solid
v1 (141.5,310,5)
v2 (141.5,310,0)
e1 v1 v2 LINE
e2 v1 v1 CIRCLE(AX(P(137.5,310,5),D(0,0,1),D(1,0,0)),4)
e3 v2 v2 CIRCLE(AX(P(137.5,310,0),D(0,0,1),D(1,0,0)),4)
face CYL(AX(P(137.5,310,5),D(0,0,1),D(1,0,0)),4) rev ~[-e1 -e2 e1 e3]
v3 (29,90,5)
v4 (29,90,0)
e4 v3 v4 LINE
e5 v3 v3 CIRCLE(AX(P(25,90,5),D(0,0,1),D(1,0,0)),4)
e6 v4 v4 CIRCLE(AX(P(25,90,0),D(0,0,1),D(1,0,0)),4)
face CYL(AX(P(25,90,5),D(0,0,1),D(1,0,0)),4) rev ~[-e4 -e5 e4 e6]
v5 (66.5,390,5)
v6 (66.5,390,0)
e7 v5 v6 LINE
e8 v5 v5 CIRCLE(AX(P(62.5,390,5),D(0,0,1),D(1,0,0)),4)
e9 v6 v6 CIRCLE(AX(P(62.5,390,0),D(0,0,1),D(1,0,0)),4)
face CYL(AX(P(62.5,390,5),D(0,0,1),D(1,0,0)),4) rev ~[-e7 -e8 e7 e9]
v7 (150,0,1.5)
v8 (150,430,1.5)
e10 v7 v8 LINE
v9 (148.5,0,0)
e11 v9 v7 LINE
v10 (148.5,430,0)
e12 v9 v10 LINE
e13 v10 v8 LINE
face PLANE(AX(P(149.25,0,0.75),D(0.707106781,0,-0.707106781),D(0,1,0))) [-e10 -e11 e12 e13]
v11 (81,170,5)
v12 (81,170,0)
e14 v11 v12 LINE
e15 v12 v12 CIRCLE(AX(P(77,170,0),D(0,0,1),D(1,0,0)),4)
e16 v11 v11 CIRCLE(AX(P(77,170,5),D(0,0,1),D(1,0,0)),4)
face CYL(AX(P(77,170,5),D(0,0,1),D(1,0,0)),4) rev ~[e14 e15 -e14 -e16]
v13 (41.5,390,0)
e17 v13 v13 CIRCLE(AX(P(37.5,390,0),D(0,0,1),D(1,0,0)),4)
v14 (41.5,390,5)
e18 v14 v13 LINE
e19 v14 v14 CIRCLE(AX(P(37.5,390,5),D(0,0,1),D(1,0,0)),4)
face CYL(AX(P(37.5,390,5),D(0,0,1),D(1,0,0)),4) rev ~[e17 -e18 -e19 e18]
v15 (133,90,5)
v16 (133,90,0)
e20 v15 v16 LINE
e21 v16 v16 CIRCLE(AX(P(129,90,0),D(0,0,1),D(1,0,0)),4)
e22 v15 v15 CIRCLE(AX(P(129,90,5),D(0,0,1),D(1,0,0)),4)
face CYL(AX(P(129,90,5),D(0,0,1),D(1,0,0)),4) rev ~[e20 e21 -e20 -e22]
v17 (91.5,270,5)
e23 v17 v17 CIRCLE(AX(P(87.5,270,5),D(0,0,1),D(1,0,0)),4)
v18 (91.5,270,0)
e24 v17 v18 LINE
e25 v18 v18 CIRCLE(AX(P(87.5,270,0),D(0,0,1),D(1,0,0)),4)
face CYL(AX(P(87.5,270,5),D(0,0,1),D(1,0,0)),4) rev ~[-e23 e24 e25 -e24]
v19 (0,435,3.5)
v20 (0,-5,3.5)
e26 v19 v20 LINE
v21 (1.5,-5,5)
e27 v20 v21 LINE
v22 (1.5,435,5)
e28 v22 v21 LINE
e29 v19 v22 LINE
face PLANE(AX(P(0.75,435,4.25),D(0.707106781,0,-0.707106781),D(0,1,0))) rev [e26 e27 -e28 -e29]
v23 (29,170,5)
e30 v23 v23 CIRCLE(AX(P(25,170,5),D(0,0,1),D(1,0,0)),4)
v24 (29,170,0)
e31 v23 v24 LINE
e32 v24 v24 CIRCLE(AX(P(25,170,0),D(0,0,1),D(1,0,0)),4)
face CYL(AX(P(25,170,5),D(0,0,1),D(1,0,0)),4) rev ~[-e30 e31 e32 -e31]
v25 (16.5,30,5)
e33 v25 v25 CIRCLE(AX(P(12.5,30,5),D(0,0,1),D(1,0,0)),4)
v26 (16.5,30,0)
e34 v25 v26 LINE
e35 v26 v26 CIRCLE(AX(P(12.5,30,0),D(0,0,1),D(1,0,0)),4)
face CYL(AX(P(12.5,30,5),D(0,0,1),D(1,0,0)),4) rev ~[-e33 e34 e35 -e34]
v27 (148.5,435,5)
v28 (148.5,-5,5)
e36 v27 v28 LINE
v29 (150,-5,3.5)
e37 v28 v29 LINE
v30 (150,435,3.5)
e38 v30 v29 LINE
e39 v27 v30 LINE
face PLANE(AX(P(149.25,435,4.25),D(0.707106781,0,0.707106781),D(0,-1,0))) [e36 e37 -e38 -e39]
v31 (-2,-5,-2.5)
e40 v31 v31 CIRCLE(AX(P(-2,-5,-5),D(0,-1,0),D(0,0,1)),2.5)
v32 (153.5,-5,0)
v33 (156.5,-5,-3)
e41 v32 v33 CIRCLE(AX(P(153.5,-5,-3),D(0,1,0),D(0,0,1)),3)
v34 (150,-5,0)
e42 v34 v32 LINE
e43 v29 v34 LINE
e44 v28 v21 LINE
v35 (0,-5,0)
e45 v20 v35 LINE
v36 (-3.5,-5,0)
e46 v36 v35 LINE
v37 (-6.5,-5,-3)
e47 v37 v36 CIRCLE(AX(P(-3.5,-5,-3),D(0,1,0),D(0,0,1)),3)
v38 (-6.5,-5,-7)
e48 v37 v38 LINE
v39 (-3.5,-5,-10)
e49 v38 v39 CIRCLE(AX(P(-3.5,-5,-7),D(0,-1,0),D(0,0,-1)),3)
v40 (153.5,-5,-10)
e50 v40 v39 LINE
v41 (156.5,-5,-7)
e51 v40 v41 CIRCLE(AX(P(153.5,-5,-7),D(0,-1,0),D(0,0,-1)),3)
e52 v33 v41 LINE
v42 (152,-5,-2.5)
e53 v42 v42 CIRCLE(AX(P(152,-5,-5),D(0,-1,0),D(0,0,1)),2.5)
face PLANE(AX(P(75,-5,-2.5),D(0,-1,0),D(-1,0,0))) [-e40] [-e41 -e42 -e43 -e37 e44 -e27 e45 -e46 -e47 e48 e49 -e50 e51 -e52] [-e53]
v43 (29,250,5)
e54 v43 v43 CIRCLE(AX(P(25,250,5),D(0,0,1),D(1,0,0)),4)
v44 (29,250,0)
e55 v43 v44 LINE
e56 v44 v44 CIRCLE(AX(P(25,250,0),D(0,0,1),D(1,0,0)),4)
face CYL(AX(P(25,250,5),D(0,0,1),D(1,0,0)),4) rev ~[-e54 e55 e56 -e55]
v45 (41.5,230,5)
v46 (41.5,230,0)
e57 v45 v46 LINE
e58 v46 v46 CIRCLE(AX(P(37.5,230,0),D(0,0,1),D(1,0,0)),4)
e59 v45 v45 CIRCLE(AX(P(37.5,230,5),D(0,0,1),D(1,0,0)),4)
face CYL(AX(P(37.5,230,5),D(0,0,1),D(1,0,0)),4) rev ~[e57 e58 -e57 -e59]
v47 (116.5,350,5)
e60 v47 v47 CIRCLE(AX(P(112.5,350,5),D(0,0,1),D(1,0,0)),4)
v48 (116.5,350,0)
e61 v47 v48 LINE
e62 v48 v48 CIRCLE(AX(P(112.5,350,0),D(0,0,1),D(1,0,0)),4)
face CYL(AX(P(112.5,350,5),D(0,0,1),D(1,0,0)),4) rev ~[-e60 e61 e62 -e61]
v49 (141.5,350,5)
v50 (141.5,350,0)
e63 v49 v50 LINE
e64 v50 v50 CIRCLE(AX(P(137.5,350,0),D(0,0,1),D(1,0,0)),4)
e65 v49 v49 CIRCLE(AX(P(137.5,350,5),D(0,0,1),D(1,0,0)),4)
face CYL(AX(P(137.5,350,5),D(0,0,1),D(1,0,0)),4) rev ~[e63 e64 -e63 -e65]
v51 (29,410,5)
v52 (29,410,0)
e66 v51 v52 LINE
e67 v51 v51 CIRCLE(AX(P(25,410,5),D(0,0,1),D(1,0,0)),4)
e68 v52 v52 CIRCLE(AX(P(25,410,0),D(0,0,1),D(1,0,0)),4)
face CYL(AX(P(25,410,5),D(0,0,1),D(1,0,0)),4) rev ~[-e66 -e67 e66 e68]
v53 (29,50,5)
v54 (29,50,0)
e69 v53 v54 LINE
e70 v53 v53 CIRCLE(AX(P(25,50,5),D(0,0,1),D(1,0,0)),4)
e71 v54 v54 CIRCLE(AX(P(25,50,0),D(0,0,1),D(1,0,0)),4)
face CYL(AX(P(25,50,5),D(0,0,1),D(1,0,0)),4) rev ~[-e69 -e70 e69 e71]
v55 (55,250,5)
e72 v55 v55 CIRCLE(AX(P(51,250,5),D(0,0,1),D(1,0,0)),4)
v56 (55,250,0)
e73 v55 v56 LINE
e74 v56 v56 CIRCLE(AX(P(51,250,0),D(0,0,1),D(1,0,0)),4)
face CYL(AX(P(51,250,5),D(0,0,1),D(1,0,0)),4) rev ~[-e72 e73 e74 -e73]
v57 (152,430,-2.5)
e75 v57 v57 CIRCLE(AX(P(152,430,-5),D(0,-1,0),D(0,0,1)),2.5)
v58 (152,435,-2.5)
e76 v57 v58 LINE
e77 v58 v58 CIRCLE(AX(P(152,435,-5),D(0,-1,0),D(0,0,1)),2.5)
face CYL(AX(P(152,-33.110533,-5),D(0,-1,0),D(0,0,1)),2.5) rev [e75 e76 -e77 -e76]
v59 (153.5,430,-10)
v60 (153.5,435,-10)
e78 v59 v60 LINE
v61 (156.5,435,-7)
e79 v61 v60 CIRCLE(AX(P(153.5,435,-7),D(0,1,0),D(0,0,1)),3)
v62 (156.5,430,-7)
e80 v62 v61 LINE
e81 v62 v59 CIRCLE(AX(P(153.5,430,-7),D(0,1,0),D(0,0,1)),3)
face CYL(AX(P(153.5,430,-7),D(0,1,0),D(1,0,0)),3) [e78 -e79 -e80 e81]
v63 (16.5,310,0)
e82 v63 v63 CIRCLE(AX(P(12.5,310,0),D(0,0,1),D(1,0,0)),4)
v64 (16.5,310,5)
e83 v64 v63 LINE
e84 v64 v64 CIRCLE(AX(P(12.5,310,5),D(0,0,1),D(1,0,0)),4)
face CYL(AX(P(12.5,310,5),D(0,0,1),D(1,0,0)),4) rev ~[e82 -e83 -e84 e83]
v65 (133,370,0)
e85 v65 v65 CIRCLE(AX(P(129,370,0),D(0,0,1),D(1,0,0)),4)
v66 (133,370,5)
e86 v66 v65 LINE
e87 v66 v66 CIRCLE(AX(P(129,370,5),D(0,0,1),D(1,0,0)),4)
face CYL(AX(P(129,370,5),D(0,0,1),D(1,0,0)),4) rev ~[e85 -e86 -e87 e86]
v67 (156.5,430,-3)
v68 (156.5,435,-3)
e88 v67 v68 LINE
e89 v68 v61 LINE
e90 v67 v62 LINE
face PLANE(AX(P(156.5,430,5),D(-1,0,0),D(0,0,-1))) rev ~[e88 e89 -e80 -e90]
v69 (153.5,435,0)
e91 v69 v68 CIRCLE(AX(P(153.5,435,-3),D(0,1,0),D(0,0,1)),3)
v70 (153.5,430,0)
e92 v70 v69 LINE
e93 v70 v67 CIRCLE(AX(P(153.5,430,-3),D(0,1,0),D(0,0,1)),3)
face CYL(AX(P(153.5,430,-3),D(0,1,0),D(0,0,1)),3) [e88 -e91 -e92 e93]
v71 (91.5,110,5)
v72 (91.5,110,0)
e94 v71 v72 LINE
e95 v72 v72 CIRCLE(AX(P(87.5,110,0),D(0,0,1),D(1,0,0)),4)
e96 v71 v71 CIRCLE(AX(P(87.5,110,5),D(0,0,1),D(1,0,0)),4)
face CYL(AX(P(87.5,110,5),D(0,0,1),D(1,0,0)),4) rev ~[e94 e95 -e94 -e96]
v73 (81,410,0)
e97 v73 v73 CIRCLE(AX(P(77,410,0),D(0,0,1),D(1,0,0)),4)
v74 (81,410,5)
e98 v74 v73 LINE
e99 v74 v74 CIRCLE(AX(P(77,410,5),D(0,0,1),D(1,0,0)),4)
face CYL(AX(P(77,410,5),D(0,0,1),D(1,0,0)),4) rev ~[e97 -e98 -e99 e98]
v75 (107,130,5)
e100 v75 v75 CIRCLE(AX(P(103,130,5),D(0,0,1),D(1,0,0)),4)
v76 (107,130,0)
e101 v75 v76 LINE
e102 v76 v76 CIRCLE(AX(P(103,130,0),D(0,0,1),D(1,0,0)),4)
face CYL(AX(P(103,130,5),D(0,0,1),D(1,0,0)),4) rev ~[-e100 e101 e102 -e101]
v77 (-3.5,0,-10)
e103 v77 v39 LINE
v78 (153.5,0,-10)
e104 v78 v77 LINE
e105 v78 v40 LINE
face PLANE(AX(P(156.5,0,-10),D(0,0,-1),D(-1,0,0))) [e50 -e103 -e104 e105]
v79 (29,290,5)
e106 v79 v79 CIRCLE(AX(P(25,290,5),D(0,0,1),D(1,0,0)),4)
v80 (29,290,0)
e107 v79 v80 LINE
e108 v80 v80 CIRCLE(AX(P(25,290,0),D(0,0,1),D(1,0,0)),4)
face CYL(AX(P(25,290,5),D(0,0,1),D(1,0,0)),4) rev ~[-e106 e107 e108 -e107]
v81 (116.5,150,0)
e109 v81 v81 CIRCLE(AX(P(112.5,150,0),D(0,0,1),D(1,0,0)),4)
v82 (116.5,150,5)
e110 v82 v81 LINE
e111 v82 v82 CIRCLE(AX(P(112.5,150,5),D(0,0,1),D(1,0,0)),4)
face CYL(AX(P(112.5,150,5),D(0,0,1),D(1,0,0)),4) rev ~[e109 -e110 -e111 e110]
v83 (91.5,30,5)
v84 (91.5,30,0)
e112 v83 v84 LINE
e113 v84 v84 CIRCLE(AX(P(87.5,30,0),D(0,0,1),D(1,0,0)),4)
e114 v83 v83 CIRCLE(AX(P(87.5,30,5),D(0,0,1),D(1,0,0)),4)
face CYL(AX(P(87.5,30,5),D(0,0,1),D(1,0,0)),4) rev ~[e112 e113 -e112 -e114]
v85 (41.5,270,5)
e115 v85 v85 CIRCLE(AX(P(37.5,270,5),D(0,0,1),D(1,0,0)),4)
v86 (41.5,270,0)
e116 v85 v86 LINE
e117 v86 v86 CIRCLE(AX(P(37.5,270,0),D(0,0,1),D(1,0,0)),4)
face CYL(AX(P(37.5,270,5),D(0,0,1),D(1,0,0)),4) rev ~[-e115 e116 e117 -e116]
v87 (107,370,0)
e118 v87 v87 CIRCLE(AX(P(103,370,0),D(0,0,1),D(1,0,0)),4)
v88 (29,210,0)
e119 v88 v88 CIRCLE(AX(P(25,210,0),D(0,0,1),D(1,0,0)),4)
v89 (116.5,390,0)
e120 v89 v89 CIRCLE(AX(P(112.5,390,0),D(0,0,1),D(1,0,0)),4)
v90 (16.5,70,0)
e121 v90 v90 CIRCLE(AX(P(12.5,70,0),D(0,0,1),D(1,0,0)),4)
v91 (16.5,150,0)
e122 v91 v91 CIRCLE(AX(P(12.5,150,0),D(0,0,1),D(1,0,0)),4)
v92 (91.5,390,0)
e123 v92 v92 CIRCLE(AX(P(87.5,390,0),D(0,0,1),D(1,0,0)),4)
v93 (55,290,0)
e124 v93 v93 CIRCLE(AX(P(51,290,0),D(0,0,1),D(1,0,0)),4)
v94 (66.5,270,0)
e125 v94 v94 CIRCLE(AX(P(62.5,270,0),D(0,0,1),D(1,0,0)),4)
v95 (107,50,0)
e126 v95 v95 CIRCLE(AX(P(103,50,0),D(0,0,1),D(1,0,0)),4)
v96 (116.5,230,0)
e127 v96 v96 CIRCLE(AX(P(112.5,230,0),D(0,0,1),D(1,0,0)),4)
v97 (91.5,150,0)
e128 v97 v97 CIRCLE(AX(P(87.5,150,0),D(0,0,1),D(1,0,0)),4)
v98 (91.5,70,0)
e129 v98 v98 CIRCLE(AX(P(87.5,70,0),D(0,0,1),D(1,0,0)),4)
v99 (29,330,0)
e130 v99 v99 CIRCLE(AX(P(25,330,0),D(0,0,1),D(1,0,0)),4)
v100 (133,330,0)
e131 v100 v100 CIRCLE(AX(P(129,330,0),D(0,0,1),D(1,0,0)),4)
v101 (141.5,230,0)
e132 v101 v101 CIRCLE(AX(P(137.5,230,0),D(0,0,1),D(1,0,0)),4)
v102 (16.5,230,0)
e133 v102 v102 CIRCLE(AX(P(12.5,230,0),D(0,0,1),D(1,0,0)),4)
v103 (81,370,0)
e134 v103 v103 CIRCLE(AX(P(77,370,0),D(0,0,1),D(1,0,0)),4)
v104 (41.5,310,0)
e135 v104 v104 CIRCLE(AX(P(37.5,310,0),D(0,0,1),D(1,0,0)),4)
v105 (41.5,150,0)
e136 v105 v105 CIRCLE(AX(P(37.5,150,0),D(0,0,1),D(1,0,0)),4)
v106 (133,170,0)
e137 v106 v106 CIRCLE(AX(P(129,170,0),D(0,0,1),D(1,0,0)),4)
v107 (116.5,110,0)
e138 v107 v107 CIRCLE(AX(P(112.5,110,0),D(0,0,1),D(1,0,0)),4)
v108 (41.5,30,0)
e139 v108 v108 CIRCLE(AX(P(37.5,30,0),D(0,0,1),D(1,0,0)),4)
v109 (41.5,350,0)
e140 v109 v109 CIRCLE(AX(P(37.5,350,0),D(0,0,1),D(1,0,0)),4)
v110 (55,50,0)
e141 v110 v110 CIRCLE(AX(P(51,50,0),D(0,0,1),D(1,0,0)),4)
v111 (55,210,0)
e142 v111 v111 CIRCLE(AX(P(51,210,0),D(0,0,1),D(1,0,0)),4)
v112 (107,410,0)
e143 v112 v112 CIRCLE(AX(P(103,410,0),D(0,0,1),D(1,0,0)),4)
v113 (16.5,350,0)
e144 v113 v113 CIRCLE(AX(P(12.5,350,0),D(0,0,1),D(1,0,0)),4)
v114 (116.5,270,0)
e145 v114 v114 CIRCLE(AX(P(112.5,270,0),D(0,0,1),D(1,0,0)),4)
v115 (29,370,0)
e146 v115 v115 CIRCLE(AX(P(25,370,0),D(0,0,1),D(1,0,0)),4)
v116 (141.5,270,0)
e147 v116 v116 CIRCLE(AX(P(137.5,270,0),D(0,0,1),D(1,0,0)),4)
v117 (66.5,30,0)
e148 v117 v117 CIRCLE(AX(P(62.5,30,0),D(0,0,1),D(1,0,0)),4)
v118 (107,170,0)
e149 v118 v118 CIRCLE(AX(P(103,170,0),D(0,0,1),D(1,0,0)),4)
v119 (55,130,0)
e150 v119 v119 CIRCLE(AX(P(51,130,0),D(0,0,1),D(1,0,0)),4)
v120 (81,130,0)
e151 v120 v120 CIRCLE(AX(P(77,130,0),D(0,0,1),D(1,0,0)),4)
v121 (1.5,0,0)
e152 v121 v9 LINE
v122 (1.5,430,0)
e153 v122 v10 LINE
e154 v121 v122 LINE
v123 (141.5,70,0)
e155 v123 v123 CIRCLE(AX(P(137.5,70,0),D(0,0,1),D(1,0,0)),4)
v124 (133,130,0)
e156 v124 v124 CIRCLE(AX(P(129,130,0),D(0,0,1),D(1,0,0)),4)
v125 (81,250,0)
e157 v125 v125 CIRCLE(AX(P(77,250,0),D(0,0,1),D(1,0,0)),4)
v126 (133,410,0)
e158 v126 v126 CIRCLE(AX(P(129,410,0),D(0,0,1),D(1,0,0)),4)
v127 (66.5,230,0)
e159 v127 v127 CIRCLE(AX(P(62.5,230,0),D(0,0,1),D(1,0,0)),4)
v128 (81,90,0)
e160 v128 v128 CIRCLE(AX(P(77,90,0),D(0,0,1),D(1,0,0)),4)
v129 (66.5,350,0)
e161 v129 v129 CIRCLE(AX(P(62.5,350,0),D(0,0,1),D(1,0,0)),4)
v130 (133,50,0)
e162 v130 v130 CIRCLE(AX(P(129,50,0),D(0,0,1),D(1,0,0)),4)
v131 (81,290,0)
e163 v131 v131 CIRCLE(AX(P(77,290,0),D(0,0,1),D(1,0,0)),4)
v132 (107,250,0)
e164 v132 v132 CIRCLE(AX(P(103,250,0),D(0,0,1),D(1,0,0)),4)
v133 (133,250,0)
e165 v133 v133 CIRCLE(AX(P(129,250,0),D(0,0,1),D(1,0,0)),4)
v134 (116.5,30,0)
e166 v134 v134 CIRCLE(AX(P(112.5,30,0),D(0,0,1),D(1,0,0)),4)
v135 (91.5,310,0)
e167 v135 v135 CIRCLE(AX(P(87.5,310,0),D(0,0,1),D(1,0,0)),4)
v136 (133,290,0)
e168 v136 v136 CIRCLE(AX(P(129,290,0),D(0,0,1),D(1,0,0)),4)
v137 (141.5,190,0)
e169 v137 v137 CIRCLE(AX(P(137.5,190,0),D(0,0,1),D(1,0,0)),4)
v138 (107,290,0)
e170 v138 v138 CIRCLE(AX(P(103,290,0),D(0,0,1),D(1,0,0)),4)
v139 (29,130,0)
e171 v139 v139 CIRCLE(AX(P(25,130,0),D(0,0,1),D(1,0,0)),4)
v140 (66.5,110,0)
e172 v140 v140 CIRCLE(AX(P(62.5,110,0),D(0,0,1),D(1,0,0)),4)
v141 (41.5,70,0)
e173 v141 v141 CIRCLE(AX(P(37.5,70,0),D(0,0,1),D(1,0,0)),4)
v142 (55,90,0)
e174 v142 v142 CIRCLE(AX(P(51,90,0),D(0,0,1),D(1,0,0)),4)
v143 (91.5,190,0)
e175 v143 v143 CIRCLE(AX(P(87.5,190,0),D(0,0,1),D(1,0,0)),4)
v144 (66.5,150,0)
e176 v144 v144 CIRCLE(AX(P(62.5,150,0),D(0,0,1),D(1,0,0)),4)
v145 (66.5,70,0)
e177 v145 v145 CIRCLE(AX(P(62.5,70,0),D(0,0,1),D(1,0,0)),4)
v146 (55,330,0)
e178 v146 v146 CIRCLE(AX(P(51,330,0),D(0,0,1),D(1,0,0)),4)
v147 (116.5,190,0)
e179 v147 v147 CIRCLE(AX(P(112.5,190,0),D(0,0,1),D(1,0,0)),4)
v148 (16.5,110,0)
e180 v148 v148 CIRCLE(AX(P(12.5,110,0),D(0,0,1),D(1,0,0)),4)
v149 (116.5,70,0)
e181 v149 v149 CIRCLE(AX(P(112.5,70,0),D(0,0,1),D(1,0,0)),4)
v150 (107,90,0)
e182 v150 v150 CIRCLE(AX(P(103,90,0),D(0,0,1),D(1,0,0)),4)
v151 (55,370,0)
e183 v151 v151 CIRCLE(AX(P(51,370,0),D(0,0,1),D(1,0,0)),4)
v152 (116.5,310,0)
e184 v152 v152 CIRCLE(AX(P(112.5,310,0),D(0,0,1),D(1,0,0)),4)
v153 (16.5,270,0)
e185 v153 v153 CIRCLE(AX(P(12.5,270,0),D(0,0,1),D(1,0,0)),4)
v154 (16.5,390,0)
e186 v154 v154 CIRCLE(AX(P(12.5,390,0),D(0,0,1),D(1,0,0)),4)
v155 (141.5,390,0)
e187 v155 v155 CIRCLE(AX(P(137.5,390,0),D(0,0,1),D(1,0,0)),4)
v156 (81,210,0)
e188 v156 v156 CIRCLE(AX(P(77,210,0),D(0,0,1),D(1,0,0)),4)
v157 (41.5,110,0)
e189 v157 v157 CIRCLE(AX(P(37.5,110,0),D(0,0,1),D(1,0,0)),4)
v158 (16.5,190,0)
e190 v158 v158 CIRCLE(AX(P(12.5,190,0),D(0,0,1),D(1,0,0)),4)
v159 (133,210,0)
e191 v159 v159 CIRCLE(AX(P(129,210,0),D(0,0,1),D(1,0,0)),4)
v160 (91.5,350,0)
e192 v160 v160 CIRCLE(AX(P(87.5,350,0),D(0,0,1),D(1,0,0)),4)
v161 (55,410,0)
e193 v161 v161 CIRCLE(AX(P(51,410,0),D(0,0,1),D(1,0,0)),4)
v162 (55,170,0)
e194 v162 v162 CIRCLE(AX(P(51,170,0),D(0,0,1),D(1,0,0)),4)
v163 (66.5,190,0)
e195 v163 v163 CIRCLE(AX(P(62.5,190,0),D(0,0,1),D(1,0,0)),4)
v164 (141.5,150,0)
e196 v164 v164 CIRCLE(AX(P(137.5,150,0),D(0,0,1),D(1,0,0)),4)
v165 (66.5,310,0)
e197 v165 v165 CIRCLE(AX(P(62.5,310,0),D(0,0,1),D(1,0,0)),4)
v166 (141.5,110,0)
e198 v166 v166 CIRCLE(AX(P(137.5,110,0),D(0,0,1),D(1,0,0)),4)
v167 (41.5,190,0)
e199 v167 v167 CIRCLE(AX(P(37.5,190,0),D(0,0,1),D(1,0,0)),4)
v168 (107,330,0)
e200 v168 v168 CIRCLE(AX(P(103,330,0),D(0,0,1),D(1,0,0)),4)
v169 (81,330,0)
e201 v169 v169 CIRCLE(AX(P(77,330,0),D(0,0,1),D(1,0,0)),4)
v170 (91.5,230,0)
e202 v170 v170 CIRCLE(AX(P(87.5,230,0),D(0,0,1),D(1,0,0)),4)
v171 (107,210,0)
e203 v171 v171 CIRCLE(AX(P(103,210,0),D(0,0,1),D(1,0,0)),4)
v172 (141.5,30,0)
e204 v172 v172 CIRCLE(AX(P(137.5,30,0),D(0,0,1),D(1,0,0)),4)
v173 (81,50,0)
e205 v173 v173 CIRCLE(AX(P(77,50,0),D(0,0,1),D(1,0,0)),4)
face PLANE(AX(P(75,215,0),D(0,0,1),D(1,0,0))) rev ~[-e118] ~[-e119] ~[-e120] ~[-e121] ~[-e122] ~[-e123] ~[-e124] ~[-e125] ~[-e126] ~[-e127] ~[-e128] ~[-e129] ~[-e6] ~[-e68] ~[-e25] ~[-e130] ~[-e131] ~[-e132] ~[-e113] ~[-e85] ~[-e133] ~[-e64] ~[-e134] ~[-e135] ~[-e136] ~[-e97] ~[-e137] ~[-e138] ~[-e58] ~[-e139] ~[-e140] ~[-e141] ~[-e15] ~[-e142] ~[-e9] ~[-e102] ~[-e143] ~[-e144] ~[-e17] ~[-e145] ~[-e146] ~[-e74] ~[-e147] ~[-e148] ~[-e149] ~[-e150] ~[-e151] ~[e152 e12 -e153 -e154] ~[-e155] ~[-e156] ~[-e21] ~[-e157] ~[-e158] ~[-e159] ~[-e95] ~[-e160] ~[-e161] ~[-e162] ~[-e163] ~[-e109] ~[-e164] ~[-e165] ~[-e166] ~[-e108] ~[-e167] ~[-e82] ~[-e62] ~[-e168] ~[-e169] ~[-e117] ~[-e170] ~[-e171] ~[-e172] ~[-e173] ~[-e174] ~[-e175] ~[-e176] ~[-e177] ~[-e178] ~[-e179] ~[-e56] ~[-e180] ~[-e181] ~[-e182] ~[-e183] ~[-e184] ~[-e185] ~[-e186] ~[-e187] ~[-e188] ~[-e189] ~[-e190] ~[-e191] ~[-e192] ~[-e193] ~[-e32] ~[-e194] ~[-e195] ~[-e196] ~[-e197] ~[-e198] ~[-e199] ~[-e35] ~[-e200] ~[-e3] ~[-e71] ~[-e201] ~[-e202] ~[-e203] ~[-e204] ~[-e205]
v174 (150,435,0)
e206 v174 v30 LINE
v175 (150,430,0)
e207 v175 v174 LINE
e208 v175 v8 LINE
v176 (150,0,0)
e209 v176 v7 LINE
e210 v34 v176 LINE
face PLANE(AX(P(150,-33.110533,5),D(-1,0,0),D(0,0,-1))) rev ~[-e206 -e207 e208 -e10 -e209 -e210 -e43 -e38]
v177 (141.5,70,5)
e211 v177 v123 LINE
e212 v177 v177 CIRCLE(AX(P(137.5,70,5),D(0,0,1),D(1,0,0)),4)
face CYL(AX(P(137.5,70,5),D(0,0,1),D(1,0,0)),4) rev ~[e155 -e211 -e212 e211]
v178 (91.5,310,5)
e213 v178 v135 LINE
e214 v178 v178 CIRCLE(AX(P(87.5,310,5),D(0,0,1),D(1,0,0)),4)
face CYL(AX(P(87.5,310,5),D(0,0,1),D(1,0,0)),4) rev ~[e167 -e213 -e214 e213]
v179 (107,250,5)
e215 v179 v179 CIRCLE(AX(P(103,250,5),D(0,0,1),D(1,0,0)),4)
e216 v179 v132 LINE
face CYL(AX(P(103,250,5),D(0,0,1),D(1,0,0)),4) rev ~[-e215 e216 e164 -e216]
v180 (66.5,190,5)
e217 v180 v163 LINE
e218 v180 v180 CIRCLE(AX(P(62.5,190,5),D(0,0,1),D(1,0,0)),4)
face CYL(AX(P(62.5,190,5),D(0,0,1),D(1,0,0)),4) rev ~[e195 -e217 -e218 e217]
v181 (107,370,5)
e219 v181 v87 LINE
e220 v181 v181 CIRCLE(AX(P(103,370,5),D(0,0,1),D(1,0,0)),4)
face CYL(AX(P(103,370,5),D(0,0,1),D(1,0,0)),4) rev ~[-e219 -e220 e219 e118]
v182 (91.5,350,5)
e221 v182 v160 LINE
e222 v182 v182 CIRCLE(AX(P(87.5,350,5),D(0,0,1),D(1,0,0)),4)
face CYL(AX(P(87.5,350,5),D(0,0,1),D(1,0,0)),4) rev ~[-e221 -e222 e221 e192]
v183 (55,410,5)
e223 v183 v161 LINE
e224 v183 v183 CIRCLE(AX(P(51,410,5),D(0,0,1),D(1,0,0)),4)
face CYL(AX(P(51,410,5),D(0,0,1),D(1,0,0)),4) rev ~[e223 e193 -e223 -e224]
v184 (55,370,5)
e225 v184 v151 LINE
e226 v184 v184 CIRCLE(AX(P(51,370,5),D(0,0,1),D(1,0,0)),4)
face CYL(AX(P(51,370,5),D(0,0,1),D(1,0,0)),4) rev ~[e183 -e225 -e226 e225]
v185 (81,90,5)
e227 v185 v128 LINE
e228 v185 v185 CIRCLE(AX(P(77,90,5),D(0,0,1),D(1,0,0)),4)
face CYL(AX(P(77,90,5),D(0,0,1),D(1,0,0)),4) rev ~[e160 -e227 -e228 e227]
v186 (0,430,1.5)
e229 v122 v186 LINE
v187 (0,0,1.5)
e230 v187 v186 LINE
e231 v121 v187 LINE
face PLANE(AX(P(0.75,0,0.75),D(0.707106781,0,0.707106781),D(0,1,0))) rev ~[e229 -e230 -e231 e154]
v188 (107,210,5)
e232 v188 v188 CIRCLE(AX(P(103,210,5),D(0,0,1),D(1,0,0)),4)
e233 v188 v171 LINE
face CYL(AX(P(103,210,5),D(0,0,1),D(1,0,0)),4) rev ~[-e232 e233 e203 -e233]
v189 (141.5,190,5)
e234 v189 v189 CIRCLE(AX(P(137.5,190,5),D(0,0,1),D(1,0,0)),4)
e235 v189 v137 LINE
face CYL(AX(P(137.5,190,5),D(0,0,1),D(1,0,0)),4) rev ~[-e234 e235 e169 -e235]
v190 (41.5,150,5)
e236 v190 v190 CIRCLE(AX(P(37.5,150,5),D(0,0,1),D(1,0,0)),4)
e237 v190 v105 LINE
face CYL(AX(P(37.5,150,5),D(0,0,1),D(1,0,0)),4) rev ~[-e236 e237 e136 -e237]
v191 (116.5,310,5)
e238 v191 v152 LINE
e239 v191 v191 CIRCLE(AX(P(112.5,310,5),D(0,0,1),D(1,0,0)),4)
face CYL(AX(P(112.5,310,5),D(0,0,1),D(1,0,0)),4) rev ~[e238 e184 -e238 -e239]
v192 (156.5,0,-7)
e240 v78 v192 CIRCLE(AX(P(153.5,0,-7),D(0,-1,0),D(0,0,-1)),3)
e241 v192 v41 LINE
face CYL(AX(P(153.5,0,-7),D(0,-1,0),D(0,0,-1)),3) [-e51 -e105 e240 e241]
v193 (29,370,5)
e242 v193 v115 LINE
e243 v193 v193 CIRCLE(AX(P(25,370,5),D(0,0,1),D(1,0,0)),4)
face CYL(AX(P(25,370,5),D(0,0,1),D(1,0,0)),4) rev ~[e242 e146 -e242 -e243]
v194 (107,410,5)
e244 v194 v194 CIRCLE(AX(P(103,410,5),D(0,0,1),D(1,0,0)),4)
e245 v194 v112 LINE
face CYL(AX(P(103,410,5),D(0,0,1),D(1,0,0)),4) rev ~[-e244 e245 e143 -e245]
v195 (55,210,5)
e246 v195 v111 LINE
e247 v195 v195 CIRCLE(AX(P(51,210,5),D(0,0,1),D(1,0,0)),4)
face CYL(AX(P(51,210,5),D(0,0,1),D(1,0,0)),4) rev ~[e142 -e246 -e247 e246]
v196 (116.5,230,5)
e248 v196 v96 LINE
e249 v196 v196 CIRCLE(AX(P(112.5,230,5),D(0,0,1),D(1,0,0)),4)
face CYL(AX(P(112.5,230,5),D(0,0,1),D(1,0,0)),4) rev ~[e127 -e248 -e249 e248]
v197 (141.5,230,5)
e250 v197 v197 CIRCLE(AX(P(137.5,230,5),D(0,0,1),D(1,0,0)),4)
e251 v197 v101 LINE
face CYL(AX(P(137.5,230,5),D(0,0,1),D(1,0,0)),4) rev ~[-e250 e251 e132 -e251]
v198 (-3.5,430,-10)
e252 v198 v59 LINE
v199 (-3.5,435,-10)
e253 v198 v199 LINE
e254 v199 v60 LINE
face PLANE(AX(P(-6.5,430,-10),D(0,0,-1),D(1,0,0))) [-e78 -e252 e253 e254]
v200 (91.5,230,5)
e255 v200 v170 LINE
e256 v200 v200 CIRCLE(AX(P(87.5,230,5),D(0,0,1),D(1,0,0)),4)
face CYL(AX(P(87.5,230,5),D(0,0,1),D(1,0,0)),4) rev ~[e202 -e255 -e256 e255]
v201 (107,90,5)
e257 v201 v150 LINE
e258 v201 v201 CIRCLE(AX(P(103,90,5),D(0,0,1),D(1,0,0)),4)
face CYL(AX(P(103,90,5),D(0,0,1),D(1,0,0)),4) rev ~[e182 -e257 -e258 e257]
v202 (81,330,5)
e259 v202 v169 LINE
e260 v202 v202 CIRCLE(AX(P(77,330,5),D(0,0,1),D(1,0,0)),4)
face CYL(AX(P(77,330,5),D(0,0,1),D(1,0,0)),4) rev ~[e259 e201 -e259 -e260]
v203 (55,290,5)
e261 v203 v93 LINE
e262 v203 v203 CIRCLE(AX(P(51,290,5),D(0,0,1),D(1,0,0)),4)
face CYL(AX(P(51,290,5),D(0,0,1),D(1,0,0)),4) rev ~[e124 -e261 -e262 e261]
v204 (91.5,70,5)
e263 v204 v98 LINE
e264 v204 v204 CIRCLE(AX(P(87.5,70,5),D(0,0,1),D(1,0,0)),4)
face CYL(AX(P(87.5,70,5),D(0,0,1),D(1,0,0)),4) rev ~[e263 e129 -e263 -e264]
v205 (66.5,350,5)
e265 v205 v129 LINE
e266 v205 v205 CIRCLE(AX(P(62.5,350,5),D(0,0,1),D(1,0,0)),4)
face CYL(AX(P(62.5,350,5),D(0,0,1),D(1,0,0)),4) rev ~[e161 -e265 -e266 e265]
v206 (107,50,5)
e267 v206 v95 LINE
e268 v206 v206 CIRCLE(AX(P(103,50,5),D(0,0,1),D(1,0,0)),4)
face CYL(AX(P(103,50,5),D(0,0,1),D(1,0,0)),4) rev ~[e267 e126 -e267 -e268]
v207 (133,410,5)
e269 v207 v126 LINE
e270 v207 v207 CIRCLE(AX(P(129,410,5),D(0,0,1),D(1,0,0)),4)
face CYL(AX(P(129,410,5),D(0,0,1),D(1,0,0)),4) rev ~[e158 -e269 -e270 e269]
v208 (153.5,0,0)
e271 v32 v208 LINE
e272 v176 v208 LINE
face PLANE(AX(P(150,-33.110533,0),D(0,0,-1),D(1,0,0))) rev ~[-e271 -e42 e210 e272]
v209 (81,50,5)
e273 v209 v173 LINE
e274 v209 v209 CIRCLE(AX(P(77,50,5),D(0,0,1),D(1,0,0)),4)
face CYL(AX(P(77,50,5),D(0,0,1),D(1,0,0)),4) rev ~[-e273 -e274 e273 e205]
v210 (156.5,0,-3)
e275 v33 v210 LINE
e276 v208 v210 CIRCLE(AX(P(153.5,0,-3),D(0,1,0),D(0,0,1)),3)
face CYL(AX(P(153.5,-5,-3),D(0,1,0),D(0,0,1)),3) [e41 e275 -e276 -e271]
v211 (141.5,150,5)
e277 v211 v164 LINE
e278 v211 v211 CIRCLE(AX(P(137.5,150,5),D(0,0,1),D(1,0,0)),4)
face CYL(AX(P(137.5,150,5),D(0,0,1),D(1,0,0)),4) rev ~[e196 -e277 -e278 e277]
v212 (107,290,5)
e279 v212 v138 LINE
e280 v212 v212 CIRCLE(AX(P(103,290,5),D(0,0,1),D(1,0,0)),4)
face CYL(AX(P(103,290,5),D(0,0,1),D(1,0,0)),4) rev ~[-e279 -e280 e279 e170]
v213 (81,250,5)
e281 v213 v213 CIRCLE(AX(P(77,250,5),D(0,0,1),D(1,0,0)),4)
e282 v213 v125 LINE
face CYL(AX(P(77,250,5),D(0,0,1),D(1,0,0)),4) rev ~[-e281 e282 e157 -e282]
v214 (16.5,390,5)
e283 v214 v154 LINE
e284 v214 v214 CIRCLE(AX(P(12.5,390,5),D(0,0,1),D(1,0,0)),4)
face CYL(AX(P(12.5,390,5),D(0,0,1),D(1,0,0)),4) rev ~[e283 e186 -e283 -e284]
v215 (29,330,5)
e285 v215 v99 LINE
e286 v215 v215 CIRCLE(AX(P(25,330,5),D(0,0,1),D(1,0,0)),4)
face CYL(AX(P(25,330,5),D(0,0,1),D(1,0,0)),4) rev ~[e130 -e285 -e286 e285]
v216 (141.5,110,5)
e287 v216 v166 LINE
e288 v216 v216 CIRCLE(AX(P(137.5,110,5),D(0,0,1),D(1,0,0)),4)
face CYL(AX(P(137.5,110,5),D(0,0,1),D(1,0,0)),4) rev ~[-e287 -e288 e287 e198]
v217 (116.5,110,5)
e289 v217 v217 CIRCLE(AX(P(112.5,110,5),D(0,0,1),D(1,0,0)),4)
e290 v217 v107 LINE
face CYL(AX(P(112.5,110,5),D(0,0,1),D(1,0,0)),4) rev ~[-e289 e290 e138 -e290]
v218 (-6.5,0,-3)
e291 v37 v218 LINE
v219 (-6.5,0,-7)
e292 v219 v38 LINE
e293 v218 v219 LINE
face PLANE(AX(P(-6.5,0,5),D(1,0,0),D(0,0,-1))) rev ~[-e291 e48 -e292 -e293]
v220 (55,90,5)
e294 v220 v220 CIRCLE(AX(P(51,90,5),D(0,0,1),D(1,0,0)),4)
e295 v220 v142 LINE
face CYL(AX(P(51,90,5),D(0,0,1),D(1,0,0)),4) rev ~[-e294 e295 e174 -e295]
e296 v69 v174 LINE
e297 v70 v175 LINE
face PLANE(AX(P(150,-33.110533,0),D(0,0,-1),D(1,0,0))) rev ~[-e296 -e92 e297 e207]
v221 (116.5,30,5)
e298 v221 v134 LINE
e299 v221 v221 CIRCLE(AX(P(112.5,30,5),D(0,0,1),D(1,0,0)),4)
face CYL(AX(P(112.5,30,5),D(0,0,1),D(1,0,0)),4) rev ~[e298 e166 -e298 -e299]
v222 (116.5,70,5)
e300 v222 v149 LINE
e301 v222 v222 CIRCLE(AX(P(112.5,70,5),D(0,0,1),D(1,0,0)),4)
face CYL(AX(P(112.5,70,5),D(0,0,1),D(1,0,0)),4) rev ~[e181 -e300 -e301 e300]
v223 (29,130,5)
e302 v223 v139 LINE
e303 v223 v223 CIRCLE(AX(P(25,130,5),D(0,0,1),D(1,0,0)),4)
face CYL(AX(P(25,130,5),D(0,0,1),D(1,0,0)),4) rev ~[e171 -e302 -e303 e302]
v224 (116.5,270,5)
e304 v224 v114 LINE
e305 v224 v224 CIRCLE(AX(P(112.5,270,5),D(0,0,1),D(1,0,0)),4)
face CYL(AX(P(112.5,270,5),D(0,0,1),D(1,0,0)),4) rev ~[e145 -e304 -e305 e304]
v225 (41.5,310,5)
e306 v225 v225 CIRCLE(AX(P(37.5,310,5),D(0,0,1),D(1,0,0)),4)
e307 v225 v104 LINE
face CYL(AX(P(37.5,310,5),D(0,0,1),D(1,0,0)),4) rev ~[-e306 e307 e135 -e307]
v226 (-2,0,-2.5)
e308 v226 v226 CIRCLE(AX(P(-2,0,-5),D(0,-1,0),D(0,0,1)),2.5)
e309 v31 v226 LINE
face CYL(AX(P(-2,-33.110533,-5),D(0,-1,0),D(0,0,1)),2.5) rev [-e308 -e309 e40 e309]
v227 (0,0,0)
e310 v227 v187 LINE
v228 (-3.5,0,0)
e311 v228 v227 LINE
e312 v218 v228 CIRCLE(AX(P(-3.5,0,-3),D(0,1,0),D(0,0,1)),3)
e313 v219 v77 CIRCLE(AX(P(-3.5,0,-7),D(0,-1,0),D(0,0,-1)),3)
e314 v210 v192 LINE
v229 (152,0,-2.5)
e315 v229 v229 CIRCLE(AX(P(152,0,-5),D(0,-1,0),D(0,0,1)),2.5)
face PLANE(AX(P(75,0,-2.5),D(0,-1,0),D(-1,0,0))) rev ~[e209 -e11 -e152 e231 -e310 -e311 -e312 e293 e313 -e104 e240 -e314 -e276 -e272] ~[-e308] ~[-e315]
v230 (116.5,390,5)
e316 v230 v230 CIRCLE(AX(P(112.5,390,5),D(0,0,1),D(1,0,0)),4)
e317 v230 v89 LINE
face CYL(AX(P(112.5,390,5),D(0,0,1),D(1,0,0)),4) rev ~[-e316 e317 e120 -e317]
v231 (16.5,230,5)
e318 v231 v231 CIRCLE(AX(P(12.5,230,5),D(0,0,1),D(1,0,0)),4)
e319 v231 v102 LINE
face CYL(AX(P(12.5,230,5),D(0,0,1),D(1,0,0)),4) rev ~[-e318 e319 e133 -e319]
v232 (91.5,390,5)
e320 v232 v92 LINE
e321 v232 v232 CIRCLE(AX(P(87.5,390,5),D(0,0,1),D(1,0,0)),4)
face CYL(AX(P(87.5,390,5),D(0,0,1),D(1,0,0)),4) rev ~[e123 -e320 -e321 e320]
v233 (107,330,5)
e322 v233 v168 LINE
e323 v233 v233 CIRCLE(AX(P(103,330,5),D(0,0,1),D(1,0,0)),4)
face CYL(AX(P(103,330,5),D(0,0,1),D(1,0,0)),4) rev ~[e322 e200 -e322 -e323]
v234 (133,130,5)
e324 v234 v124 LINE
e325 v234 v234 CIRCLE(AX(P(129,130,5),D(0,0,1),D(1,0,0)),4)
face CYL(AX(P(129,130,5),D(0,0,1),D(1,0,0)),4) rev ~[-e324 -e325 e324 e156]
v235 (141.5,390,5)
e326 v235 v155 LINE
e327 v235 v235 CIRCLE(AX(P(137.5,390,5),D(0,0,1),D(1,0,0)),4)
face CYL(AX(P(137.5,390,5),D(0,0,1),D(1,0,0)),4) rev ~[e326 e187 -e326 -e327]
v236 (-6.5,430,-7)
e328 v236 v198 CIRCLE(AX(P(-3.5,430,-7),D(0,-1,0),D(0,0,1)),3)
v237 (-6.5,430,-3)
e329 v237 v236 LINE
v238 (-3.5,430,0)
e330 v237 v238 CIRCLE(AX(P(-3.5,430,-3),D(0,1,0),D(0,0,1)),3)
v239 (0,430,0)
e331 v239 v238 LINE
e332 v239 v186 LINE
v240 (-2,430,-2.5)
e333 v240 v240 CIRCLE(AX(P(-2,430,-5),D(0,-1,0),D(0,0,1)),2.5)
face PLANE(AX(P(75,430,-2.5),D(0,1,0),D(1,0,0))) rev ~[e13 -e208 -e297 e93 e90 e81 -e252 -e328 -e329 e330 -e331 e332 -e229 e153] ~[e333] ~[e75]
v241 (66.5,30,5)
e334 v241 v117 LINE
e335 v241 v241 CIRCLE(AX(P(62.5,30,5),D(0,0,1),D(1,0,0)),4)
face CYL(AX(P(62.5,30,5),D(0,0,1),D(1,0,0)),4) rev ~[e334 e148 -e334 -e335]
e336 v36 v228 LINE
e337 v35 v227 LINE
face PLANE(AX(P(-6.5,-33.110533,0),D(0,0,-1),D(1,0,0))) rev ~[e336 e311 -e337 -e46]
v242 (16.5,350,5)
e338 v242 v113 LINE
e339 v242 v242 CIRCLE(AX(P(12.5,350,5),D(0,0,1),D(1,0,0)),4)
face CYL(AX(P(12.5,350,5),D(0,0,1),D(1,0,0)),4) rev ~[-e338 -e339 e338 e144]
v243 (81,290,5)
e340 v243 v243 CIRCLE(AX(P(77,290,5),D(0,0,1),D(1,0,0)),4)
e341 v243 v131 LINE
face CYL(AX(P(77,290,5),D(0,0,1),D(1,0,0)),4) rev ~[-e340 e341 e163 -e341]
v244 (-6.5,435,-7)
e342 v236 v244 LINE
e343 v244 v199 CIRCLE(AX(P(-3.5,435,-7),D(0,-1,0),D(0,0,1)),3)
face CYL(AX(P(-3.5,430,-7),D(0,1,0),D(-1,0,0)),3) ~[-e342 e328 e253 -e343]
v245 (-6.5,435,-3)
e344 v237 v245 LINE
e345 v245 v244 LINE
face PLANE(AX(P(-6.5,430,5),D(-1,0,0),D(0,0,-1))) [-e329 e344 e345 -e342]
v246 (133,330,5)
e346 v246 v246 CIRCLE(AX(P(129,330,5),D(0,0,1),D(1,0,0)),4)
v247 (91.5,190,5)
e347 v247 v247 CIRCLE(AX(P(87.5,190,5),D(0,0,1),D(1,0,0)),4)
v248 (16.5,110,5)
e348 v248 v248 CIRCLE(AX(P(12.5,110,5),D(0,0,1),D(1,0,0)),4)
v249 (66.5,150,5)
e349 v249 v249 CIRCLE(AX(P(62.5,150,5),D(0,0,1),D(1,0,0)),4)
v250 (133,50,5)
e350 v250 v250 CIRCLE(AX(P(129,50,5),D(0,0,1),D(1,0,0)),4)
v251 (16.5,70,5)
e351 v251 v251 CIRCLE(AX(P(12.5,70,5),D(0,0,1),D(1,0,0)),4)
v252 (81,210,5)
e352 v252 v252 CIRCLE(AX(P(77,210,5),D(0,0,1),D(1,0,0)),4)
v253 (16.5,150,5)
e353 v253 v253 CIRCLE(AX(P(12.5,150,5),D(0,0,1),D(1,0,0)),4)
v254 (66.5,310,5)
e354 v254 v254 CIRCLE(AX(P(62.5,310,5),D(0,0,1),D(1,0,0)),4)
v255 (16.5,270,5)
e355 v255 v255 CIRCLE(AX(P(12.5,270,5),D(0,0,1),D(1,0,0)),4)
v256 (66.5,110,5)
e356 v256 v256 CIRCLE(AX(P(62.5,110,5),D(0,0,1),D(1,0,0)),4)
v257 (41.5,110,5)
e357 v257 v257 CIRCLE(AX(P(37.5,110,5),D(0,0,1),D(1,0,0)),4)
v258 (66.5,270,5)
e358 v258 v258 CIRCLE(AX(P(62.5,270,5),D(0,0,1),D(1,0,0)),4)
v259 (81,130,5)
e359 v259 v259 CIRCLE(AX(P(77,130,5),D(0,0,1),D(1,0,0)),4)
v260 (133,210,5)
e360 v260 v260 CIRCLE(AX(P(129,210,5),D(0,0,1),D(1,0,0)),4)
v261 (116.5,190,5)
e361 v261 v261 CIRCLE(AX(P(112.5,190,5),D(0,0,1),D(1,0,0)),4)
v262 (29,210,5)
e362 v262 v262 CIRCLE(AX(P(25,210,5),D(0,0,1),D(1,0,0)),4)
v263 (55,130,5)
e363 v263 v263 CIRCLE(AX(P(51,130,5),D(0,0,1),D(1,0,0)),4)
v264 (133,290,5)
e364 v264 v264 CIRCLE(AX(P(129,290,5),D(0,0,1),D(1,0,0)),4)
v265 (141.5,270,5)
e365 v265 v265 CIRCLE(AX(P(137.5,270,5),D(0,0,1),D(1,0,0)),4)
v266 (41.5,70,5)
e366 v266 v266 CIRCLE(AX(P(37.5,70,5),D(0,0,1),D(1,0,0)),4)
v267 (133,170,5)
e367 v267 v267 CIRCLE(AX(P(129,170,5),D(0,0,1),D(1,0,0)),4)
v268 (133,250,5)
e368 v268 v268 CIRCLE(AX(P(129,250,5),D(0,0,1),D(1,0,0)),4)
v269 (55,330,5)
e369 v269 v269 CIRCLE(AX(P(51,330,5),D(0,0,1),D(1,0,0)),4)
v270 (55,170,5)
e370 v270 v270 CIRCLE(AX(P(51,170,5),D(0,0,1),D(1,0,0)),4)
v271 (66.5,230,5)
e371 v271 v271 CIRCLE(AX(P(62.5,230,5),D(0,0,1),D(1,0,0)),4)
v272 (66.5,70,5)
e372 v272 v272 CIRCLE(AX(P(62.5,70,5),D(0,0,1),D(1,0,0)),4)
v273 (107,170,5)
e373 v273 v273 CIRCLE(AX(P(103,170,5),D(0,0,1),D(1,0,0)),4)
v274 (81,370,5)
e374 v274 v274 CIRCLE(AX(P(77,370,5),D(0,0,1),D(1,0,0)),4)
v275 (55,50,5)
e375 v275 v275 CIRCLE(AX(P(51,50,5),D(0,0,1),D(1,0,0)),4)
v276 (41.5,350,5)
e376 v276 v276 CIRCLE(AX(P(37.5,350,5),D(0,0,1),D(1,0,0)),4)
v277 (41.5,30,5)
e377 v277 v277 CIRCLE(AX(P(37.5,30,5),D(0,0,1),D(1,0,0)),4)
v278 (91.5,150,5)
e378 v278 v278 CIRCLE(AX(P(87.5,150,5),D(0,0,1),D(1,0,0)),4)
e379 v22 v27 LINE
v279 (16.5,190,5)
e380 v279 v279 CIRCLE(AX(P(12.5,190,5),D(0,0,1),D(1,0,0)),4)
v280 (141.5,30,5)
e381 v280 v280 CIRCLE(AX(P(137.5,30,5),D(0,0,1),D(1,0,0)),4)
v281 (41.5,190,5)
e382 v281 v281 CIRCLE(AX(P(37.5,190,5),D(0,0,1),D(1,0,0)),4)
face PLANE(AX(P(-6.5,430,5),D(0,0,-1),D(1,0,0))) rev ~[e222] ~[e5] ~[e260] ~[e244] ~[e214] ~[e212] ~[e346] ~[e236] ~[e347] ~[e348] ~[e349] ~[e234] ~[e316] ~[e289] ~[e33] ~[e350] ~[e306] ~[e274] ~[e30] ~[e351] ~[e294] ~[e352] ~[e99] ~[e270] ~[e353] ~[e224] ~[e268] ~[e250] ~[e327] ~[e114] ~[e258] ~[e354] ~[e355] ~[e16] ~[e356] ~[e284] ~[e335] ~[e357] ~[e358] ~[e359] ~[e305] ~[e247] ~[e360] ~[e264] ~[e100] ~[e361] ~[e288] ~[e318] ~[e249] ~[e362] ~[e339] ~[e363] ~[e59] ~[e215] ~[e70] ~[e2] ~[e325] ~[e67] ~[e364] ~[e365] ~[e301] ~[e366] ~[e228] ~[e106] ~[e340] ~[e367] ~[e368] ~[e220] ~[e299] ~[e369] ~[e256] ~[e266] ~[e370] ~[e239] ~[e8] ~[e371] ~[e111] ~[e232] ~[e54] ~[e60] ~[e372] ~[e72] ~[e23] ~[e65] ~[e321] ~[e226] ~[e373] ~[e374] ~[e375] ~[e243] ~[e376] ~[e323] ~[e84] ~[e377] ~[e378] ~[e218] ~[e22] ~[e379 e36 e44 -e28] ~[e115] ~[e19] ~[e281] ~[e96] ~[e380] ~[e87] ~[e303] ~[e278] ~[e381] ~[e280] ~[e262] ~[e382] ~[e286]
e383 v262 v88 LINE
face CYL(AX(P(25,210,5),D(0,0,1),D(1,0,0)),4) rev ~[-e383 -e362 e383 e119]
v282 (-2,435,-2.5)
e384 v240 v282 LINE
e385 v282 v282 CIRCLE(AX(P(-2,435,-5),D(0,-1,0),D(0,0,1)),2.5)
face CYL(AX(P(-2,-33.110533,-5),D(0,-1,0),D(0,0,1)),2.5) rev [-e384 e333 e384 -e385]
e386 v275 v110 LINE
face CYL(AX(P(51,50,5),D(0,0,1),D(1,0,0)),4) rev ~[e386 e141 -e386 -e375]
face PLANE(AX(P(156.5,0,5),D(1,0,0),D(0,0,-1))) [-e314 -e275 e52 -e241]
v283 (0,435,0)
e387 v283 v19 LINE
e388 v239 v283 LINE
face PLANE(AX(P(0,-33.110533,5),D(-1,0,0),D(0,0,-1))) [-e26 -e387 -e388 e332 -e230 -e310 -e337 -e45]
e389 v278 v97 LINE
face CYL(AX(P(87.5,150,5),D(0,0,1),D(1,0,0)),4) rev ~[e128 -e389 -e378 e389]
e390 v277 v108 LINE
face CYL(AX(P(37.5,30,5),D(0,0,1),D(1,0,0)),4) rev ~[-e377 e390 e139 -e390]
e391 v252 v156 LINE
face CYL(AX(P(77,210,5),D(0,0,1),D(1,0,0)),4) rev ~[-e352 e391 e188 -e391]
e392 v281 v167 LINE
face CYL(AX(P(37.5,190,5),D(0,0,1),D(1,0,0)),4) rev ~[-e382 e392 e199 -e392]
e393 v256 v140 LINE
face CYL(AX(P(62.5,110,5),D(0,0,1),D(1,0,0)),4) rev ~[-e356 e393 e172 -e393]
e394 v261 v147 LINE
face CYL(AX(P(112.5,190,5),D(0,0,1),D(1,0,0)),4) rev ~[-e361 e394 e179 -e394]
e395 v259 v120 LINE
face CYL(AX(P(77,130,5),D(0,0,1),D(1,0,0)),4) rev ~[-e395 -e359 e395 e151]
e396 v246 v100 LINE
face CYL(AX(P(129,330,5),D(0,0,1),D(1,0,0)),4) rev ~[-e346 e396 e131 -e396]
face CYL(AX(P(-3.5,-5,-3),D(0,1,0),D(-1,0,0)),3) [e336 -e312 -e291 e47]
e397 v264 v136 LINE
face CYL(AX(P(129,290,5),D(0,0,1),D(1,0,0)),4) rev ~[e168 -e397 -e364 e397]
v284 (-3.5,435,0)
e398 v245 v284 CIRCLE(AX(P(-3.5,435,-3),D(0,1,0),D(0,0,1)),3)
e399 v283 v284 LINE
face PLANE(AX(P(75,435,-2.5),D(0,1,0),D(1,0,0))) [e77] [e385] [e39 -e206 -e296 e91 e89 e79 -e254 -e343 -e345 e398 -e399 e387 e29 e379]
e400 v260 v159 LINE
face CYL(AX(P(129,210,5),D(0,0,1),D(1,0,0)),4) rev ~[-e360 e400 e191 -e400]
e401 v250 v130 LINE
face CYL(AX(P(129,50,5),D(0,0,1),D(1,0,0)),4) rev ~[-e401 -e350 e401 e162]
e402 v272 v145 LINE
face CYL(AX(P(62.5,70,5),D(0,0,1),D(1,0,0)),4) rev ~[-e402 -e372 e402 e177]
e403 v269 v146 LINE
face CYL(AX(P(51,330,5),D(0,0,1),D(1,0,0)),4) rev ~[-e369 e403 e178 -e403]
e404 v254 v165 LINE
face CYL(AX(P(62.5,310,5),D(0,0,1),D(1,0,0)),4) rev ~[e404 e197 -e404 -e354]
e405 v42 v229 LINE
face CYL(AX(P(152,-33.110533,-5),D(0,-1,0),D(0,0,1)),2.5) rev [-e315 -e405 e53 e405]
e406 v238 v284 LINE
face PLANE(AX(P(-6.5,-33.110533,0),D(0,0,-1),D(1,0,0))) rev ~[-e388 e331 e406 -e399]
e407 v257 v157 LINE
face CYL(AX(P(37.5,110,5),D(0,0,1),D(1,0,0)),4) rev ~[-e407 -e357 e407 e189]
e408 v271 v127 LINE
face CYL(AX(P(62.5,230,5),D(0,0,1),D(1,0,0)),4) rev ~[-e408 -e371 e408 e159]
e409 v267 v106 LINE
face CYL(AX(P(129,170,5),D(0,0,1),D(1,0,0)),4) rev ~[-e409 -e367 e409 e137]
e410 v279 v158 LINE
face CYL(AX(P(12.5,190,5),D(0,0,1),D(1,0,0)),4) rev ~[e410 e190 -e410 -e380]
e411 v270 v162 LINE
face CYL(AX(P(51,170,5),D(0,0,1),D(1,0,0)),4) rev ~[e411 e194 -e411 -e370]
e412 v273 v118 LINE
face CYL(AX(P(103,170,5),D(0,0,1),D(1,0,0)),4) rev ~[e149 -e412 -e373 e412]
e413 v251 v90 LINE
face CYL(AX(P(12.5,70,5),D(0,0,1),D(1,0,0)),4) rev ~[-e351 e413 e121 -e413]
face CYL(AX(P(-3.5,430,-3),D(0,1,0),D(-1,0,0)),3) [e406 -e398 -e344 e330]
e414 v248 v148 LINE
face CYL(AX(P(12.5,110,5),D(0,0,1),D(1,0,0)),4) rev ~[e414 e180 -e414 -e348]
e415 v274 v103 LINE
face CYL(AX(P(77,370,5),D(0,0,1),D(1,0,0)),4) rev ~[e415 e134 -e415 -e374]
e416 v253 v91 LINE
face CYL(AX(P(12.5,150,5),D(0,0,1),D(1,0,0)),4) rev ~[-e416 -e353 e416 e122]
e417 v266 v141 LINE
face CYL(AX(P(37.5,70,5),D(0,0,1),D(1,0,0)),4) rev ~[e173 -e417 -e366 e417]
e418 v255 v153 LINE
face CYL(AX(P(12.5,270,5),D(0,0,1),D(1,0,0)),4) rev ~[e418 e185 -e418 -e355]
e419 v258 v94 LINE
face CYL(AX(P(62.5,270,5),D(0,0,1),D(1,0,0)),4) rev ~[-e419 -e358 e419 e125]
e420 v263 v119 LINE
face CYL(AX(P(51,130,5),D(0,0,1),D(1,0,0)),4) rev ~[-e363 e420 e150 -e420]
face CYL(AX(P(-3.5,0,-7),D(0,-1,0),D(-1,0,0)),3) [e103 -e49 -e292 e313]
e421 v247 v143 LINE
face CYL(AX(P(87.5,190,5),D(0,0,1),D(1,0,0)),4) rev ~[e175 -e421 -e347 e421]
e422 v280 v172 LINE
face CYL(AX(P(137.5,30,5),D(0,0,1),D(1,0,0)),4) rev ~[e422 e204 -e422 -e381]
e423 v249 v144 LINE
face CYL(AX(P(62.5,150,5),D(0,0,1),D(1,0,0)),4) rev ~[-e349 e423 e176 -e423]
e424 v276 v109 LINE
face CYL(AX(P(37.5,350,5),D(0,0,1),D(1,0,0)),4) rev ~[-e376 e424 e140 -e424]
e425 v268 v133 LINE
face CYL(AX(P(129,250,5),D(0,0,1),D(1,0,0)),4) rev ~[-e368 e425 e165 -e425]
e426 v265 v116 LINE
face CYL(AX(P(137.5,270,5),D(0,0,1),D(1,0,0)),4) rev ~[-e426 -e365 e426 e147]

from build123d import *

# Parameters (mm, degrees)
SKETCH1_W               = 150
SKETCH1_H               = 430
BOSS_EXTRUDE1_DEPTH     = 5
CUT_EXTRUDE1_REACH      = 457.439
SKETCH2_R               = 4
LPATTERN1_COUNT         = 10
LPATTERN1_PITCH         = 40
SKETCH3_W               = 163
SKETCH3_H               = 15
BOSS_EXTRUDE2_DEPTH     = 5
SKETCH4_W               = 163
SKETCH4_H               = 15
BOSS_EXTRUDE3_DEPTH     = 5
CUT_EXTRUDE2_DEPTH      = 468.110532958
CUT_EXTRUDE2_DEPTH_BACK = 468.110532958
SKETCH6_R               = 2.5
SKETCH6_W               = 6.5
SKETCH6_H               = 5
FILLET1_R               = 3
CHAMFER1_SIZE           = 1.5


with BuildPart() as part:
    # Sketch1 → Boss-Extrude1 (new body)
    with BuildSketch(Plane.XY):
        with Locations((75, 215)):
            Rectangle(SKETCH1_W, SKETCH1_H)
    extrude(amount=BOSS_EXTRUDE1_DEPTH)

    # Sketch2 → Cut-Extrude1 (cut, up to next)
    with BuildSketch(Plane.XY.offset(5), mode=Mode.PRIVATE) as cut_extrude1_sk1:
        with Locations((25, 410)):
            Circle(SKETCH2_R)
    cut_extrude1_tool1 = extrude(cut_extrude1_sk1.sketch, amount=-CUT_EXTRUDE1_REACH, mode=Mode.PRIVATE) & part.part
    # Sketch2 → Cut-Extrude1 (cut, up to next)
    with BuildSketch(Plane.XY.offset(5), mode=Mode.PRIVATE) as cut_extrude1_sk2:
        with Locations((51, 410)):
            Circle(SKETCH2_R)
    cut_extrude1_tool2 = extrude(cut_extrude1_sk2.sketch, amount=-CUT_EXTRUDE1_REACH, mode=Mode.PRIVATE) & part.part
    # Sketch2 → Cut-Extrude1 (cut, up to next)
    with BuildSketch(Plane.XY.offset(5), mode=Mode.PRIVATE) as cut_extrude1_sk3:
        with Locations((77, 410)):
            Circle(SKETCH2_R)
    cut_extrude1_tool3 = extrude(cut_extrude1_sk3.sketch, amount=-CUT_EXTRUDE1_REACH, mode=Mode.PRIVATE) & part.part
    # Sketch2 → Cut-Extrude1 (cut, up to next)
    with BuildSketch(Plane.XY.offset(5), mode=Mode.PRIVATE) as cut_extrude1_sk4:
        with Locations((103, 410)):
            Circle(SKETCH2_R)
    cut_extrude1_tool4 = extrude(cut_extrude1_sk4.sketch, amount=-CUT_EXTRUDE1_REACH, mode=Mode.PRIVATE) & part.part
    # Sketch2 → Cut-Extrude1 (cut, up to next)
    with BuildSketch(Plane.XY.offset(5), mode=Mode.PRIVATE) as cut_extrude1_sk5:
        with Locations((129, 410)):
            Circle(SKETCH2_R)
    cut_extrude1_tool5 = extrude(cut_extrude1_sk5.sketch, amount=-CUT_EXTRUDE1_REACH, mode=Mode.PRIVATE) & part.part
    # Sketch2 → Cut-Extrude1 (cut, up to next)
    with BuildSketch(Plane.XY.offset(5), mode=Mode.PRIVATE) as cut_extrude1_sk6:
        with Locations((12.5, 390)):
            Circle(SKETCH2_R)
    cut_extrude1_tool6 = extrude(cut_extrude1_sk6.sketch, amount=-CUT_EXTRUDE1_REACH, mode=Mode.PRIVATE) & part.part
    # Sketch2 → Cut-Extrude1 (cut, up to next)
    with BuildSketch(Plane.XY.offset(5), mode=Mode.PRIVATE) as cut_extrude1_sk7:
        with Locations((37.5, 390)):
            Circle(SKETCH2_R)
    cut_extrude1_tool7 = extrude(cut_extrude1_sk7.sketch, amount=-CUT_EXTRUDE1_REACH, mode=Mode.PRIVATE) & part.part
    # Sketch2 → Cut-Extrude1 (cut, up to next)
    with BuildSketch(Plane.XY.offset(5), mode=Mode.PRIVATE) as cut_extrude1_sk8:
        with Locations((62.5, 390)):
            Circle(SKETCH2_R)
    cut_extrude1_tool8 = extrude(cut_extrude1_sk8.sketch, amount=-CUT_EXTRUDE1_REACH, mode=Mode.PRIVATE) & part.part
    # Sketch2 → Cut-Extrude1 (cut, up to next)
    with BuildSketch(Plane.XY.offset(5), mode=Mode.PRIVATE) as cut_extrude1_sk9:
        with Locations((87.5, 390)):
            Circle(SKETCH2_R)
    cut_extrude1_tool9 = extrude(cut_extrude1_sk9.sketch, amount=-CUT_EXTRUDE1_REACH, mode=Mode.PRIVATE) & part.part
    # Sketch2 → Cut-Extrude1 (cut, up to next)
    with BuildSketch(Plane.XY.offset(5), mode=Mode.PRIVATE) as cut_extrude1_sk10:
        with Locations((112.5, 390)):
            Circle(SKETCH2_R)
    cut_extrude1_tool10 = extrude(cut_extrude1_sk10.sketch, amount=-CUT_EXTRUDE1_REACH, mode=Mode.PRIVATE) & part.part
    # Sketch2 → Cut-Extrude1 (cut, up to next)
    with BuildSketch(Plane.XY.offset(5), mode=Mode.PRIVATE) as cut_extrude1_sk11:
        with Locations((137.5, 390)):
            Circle(SKETCH2_R)
    cut_extrude1_tool11 = extrude(cut_extrude1_sk11.sketch, amount=-CUT_EXTRUDE1_REACH, mode=Mode.PRIVATE) & part.part
    cut_extrude1_1 = cut_extrude1_tool1.solids().sort_by_distance((25, 410, 5))[0]
    add(cut_extrude1_1, mode=Mode.SUBTRACT)
    cut_extrude1_2 = cut_extrude1_tool2.solids().sort_by_distance((51, 410, 5))[0]
    add(cut_extrude1_2, mode=Mode.SUBTRACT)
    cut_extrude1_3 = cut_extrude1_tool3.solids().sort_by_distance((77, 410, 5))[0]
    add(cut_extrude1_3, mode=Mode.SUBTRACT)
    cut_extrude1_4 = cut_extrude1_tool4.solids().sort_by_distance((103, 410, 5))[0]
    add(cut_extrude1_4, mode=Mode.SUBTRACT)
    cut_extrude1_5 = cut_extrude1_tool5.solids().sort_by_distance((129, 410, 5))[0]
    add(cut_extrude1_5, mode=Mode.SUBTRACT)
    cut_extrude1_6 = cut_extrude1_tool6.solids().sort_by_distance((12.5, 390, 5))[0]
    add(cut_extrude1_6, mode=Mode.SUBTRACT)
    cut_extrude1_7 = cut_extrude1_tool7.solids().sort_by_distance((37.5, 390, 5))[0]
    add(cut_extrude1_7, mode=Mode.SUBTRACT)
    cut_extrude1_8 = cut_extrude1_tool8.solids().sort_by_distance((62.5, 390, 5))[0]
    add(cut_extrude1_8, mode=Mode.SUBTRACT)
    cut_extrude1_9 = cut_extrude1_tool9.solids().sort_by_distance((87.5, 390, 5))[0]
    add(cut_extrude1_9, mode=Mode.SUBTRACT)
    cut_extrude1_10 = cut_extrude1_tool10.solids().sort_by_distance((112.5, 390, 5))[0]
    add(cut_extrude1_10, mode=Mode.SUBTRACT)
    cut_extrude1_11 = cut_extrude1_tool11.solids().sort_by_distance((137.5, 390, 5))[0]
    add(cut_extrude1_11, mode=Mode.SUBTRACT)
    cut_extrude1 = cut_extrude1_1 + cut_extrude1_2 + cut_extrude1_3 + cut_extrude1_4 + cut_extrude1_5 + cut_extrude1_6 + cut_extrude1_7 + cut_extrude1_8 + cut_extrude1_9 + cut_extrude1_10 + cut_extrude1_11  # Cut-Extrude1 as one shape, for the pattern or mirror that repeats it

    # LPattern1: Cut-Extrude1 ×10
    with Locations(*[(0, -i * LPATTERN1_PITCH, 0) for i in range(1, LPATTERN1_COUNT)]):
        add(cut_extrude1, mode=Mode.SUBTRACT)

    # Sketch3 → Boss-Extrude2 (add)
    with BuildSketch(Plane(origin=(0, 0, 0), x_dir=(-1, 0, 0), z_dir=(0, -1, 0))):
        with Locations((-75, 2.5)):
            Rectangle(SKETCH3_W, SKETCH3_H)
    extrude(amount=BOSS_EXTRUDE2_DEPTH)

    # Sketch4 → Boss-Extrude3 (add)
    with BuildSketch(Plane(origin=(0, 430, 0), x_dir=(1, 0, 0), z_dir=(0, 1, 0))):
        with Locations((75, 2.5)):
            Rectangle(SKETCH4_W, SKETCH4_H)
    extrude(amount=BOSS_EXTRUDE3_DEPTH)

    # Sketch6 → Cut-Extrude2 (cut, two sides: drawn at the far end of the back side and taken through both)
    with BuildSketch(Plane(origin=(0, 435, 0), x_dir=(1, 0, 0), z_dir=(0, 1, 0)).offset(-CUT_EXTRUDE2_DEPTH_BACK)):
        with Locations(Location((-2, 5, 0), (0, 0, 270))):
            Circle(SKETCH6_R)
        with Locations(Location((152, 5, 0), (0, 0, 270))):
            Circle(SKETCH6_R)
        with Locations((153.25, -2.5)):
            Rectangle(SKETCH6_W, SKETCH6_H)
        with Locations((-3.25, -2.5)):
            Rectangle(SKETCH6_W, SKETCH6_H)
    extrude(amount=CUT_EXTRUDE2_DEPTH + CUT_EXTRUDE2_DEPTH_BACK, mode=Mode.SUBTRACT)

    # Fillet1
    fillet1_edges = [part.edges().sort_by_distance(p)[0] for p in [
        (-6.5, -2.5, -10),
        (156.5, -2.5, -10),
        (-6.5, 432.5, -10),
        (156.5, 432.5, -10),
        (-6.5, 432.5, 0),
        (-6.5, -2.5, 0),
        (156.5, 432.5, 0),
        (156.5, -2.5, 0),
    ]]
    fillet(fillet1_edges, radius=FILLET1_R)

    # Chamfer1
    chamfer1_edges = [part.edges().sort_by_distance(p)[0] for p in [
        (150, 215, 5),
        (0, 215, 5),
        (150, 215, 0),
        (0, 215, 0),
    ]]
    chamfer(chamfer1_edges, length=CHAMFER1_SIZE)


solid = part.part
